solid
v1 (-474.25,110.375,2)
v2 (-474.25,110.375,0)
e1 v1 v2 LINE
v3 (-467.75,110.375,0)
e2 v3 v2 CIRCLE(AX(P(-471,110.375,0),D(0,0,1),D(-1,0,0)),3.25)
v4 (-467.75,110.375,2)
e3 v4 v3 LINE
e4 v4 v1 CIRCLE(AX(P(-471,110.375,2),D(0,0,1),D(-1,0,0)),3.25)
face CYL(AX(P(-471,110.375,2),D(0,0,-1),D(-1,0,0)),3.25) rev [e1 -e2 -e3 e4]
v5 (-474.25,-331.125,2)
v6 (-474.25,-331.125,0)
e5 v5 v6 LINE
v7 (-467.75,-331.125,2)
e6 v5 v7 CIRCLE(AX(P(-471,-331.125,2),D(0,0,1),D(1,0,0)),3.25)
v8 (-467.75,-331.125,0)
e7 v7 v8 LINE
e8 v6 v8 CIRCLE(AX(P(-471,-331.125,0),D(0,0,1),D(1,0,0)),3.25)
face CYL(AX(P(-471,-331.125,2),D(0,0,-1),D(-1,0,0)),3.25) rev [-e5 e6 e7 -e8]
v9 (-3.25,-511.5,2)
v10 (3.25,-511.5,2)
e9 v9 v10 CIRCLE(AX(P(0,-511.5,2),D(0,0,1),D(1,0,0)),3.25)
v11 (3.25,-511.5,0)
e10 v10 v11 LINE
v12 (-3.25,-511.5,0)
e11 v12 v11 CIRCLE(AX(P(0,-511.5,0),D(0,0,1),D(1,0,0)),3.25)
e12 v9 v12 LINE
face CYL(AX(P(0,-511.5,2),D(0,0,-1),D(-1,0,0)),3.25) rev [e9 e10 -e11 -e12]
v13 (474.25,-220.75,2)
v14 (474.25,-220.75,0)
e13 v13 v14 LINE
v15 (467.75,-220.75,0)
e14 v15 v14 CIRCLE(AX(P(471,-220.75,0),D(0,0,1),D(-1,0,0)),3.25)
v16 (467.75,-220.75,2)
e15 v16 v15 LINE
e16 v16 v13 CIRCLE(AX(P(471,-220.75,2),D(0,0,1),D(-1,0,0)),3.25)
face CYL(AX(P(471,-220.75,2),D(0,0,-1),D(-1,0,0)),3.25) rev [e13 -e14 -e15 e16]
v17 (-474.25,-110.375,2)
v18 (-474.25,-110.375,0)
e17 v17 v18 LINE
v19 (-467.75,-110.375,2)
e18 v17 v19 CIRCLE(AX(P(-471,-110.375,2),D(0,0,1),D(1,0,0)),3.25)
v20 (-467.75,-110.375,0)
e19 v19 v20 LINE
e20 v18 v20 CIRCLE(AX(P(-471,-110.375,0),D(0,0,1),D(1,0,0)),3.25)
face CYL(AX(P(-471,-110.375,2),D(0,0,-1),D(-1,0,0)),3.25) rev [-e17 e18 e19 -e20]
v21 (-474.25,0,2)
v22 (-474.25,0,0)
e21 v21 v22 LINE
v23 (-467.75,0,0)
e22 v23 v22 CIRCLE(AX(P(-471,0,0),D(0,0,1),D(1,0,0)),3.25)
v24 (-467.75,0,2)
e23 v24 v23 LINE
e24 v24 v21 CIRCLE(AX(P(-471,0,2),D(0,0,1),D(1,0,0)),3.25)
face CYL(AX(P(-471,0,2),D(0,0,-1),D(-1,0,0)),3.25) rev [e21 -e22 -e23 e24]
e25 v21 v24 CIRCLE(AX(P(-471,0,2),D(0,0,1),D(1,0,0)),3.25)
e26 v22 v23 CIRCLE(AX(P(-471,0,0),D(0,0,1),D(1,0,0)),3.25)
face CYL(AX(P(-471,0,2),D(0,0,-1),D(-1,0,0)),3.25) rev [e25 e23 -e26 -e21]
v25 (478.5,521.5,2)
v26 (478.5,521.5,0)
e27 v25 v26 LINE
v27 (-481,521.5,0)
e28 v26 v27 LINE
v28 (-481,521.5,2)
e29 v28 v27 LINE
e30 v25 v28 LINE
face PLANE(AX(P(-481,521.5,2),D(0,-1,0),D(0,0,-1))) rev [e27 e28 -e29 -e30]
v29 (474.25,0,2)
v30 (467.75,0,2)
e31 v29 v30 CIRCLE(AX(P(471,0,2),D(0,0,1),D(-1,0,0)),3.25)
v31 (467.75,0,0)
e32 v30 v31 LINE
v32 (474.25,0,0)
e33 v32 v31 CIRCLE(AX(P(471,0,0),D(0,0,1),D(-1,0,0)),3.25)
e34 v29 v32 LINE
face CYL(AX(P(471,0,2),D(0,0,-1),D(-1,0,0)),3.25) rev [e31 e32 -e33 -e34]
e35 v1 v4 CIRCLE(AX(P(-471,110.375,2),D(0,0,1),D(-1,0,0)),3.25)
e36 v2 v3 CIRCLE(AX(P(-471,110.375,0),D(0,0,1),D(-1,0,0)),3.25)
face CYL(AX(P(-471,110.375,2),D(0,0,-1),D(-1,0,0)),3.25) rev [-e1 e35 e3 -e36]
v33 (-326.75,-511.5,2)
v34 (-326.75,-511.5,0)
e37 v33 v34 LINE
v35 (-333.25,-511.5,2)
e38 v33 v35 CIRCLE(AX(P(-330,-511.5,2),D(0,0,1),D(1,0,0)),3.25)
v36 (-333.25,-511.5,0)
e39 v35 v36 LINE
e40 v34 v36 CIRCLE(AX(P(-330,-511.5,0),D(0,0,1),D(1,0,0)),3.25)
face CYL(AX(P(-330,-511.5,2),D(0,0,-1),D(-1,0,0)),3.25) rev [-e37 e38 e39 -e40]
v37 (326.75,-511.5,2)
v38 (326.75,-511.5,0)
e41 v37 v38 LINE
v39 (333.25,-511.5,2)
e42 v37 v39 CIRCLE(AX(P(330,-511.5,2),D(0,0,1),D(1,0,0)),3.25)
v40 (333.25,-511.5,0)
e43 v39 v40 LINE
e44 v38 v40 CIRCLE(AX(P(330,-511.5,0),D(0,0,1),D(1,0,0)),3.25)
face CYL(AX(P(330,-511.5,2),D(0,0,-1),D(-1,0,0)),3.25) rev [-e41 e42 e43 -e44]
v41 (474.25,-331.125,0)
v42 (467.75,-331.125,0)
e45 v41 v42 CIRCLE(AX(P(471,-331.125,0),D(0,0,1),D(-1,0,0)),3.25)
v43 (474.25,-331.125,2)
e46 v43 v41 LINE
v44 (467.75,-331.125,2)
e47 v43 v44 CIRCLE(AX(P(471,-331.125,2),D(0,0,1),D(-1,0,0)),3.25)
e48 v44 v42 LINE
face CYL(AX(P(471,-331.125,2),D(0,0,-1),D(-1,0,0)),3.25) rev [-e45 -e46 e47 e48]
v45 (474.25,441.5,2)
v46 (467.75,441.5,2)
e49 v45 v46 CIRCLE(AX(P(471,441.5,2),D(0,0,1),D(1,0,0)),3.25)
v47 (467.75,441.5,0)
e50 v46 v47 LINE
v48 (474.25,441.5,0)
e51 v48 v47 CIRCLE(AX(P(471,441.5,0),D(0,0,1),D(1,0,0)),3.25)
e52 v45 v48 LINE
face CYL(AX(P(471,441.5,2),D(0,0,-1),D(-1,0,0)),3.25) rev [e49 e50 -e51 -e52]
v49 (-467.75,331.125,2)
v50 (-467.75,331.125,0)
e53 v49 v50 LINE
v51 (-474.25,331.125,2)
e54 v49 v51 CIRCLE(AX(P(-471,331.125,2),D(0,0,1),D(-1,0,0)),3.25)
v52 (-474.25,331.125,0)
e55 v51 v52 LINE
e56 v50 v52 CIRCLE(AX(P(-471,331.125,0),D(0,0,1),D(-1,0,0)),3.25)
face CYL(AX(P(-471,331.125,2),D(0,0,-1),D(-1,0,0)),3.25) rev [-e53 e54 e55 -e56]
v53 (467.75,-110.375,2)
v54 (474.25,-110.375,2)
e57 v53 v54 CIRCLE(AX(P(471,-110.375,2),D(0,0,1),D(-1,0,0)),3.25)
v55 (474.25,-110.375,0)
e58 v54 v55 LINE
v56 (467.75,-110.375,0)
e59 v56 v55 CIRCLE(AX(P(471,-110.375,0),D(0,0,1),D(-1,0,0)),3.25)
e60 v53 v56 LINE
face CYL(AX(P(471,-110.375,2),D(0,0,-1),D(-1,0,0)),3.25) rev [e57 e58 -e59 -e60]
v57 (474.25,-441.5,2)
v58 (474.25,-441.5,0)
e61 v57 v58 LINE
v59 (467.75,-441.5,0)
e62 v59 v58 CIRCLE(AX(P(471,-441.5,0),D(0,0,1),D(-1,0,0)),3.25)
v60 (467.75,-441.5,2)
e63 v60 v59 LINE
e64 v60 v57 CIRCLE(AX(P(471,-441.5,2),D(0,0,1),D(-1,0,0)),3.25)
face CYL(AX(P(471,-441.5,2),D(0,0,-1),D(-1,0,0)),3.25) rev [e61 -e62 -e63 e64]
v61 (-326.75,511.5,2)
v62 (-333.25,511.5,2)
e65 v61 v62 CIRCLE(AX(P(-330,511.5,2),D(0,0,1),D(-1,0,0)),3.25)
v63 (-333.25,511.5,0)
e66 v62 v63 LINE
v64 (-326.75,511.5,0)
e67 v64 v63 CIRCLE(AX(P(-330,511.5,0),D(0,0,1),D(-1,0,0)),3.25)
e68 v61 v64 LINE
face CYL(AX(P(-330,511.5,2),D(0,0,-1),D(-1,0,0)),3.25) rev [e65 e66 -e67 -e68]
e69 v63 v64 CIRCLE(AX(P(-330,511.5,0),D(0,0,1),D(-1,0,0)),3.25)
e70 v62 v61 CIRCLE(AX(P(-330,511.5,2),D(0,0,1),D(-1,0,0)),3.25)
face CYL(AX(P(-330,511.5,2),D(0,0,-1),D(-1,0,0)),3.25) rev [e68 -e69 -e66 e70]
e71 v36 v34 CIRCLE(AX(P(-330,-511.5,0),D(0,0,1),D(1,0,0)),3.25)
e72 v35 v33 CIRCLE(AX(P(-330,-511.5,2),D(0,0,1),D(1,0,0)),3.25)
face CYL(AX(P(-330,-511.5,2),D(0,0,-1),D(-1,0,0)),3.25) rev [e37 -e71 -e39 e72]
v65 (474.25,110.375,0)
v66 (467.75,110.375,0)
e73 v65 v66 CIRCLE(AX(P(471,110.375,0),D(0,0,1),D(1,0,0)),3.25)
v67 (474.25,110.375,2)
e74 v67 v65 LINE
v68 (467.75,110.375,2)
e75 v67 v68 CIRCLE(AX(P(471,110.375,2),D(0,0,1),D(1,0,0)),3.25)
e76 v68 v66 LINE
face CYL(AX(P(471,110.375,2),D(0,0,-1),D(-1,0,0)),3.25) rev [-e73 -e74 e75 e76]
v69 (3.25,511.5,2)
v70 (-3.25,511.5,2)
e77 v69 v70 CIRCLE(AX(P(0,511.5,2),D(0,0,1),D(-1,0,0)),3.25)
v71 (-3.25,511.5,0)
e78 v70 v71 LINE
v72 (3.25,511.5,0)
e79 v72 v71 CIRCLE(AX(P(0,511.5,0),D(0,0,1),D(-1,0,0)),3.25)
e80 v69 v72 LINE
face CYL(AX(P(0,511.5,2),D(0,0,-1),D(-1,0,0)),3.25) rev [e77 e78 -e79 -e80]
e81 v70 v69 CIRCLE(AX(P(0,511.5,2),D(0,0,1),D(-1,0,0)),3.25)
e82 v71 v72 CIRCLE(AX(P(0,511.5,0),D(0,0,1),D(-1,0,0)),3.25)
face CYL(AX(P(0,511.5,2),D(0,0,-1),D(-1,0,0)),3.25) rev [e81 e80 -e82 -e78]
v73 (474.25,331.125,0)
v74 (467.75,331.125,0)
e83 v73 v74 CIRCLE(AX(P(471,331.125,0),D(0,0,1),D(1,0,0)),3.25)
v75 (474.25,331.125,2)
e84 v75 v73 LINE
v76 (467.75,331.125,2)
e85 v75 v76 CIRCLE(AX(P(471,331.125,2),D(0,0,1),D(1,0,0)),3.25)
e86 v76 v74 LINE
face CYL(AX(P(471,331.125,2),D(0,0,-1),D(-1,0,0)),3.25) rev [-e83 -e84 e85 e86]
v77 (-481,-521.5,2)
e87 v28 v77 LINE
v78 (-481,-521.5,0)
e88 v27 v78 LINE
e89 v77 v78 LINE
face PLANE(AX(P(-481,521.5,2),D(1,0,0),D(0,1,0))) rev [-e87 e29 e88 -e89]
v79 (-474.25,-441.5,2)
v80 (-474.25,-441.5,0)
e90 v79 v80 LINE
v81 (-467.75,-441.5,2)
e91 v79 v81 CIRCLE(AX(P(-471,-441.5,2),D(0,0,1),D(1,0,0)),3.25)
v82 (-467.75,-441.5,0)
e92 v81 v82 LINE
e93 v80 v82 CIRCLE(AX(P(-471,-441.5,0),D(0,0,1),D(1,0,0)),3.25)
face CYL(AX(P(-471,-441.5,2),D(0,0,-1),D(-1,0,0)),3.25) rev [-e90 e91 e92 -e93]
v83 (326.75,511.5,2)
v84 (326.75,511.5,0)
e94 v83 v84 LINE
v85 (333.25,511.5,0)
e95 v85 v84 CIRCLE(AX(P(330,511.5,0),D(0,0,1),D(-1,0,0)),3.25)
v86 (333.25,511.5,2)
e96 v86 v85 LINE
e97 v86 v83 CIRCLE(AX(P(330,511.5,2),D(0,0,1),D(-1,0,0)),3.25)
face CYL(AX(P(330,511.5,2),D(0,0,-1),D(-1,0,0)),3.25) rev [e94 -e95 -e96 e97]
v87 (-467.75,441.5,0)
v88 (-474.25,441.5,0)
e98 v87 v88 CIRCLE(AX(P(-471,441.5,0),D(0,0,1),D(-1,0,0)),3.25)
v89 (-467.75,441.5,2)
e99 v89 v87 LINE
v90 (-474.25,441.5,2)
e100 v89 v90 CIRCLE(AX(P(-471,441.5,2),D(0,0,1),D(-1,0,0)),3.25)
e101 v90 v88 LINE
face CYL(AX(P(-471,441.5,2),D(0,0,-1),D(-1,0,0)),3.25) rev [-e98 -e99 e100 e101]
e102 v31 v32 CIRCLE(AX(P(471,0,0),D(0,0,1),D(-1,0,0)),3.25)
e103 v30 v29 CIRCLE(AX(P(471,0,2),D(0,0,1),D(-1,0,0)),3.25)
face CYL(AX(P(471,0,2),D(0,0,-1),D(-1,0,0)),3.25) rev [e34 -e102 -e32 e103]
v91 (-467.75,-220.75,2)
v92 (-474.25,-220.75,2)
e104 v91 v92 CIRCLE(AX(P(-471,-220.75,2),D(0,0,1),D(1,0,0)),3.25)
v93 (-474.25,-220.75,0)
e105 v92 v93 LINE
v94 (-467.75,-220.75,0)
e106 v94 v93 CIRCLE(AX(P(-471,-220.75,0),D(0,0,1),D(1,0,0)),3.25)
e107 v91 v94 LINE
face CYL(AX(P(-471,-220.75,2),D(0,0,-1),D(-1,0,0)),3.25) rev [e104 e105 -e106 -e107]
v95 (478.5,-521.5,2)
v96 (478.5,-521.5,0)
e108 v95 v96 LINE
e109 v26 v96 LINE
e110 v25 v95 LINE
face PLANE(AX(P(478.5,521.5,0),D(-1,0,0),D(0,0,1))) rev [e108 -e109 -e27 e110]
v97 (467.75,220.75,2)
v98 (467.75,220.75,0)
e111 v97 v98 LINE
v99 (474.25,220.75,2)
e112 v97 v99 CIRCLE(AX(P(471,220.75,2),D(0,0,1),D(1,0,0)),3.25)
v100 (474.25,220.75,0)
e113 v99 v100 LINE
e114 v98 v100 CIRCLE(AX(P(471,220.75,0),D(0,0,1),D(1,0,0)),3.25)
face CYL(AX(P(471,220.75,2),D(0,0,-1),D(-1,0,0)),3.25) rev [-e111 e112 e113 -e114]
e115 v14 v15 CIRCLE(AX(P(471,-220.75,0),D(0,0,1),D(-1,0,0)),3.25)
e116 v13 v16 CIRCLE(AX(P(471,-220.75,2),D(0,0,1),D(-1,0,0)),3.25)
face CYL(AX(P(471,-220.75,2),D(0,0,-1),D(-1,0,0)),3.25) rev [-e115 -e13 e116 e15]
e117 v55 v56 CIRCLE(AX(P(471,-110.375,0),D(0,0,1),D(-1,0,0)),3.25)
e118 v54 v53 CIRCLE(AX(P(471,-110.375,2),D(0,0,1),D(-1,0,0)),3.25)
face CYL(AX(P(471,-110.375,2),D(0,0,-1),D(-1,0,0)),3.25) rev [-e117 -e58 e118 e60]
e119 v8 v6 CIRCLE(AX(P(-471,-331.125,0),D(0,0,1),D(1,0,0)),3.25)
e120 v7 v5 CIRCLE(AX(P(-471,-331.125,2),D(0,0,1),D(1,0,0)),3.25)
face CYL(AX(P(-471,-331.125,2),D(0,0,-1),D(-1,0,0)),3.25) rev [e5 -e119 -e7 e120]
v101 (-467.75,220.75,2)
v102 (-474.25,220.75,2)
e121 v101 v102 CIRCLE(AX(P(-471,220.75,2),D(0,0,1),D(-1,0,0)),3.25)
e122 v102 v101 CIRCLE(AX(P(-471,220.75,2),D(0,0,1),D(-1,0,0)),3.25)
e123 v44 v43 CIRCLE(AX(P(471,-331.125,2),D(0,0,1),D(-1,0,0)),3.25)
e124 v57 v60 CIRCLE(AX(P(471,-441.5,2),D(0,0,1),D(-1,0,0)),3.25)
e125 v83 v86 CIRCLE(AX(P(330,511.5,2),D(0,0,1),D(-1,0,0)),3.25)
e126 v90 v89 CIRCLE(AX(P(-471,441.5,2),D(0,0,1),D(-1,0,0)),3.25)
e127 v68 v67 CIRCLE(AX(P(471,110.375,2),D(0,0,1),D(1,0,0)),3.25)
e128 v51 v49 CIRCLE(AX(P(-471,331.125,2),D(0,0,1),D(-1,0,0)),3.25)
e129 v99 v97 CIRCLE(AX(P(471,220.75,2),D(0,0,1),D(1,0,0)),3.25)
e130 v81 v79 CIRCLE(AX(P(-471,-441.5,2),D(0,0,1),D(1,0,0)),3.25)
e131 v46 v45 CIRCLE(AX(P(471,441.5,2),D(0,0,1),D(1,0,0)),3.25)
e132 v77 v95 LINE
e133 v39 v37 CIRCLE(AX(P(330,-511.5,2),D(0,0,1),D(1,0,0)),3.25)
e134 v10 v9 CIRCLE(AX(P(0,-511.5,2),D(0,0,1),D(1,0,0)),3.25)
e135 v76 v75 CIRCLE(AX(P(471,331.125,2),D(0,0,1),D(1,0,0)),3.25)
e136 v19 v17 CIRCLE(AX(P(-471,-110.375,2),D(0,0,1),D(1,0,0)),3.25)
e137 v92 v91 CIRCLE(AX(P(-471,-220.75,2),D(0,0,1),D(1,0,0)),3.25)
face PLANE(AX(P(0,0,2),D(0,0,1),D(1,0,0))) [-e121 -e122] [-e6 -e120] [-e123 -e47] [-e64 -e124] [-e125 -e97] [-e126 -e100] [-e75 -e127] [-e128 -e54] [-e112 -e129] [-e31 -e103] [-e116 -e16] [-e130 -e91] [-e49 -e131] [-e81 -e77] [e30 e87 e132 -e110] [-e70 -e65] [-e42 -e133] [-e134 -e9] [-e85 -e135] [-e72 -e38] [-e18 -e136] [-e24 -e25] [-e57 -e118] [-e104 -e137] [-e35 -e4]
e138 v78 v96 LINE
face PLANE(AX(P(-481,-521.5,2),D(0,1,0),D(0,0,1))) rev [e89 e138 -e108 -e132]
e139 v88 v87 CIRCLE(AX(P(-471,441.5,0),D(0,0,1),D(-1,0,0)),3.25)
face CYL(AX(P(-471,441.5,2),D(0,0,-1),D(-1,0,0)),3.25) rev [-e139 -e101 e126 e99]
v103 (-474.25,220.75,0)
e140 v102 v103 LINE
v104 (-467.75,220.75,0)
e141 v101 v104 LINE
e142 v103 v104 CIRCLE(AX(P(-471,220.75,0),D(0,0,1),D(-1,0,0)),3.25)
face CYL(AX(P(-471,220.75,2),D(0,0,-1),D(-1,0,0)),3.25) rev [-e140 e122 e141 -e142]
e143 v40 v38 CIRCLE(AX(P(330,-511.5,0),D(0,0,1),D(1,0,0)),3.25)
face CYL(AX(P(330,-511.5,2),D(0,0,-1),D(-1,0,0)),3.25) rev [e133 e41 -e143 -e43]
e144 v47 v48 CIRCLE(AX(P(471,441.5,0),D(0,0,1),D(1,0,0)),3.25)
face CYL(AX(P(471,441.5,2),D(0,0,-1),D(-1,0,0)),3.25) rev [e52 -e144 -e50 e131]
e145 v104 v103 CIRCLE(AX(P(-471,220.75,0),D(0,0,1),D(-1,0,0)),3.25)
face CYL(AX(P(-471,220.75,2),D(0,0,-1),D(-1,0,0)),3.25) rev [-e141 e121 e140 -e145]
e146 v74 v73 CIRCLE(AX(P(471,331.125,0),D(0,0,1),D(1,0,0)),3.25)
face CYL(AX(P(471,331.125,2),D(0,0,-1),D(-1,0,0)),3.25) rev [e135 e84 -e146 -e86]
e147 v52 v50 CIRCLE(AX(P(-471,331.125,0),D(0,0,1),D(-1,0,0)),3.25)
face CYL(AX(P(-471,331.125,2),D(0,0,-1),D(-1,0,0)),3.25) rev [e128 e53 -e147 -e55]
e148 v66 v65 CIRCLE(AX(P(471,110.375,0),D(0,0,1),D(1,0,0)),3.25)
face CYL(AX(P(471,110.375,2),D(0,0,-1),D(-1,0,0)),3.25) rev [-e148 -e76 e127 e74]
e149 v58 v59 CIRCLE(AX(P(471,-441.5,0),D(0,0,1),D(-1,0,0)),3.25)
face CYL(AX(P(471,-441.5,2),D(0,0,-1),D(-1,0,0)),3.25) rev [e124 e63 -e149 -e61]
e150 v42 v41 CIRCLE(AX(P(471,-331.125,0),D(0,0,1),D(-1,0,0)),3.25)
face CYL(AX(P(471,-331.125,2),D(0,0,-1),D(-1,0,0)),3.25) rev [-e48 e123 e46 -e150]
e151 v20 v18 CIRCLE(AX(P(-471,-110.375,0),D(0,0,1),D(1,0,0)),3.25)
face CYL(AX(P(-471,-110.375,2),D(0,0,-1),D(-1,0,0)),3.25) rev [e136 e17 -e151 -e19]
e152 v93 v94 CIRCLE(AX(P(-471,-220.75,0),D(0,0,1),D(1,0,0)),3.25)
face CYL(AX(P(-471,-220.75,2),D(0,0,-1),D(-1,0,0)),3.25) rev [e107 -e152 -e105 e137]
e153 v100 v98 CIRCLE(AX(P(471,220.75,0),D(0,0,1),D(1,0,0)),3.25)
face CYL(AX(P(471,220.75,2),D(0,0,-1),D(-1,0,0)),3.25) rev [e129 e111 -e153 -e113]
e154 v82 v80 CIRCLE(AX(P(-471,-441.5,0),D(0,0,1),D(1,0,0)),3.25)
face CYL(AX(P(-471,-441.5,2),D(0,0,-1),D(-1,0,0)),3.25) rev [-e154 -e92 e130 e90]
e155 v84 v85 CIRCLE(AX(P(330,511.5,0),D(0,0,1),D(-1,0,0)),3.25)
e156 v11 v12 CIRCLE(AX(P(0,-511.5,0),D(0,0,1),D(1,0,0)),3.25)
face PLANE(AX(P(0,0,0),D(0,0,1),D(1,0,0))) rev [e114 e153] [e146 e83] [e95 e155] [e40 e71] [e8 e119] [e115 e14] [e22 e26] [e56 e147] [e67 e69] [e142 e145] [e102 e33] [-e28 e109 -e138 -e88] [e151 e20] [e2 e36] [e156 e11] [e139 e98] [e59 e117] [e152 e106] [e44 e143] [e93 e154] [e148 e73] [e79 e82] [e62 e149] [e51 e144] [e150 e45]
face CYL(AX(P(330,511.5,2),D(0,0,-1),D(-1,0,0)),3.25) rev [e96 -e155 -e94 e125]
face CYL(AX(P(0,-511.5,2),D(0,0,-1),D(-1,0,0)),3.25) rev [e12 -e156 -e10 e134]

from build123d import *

# Parameters (mm, degrees)
SKETCH_1_W          = 962
SKETCH_1_H          = 1043
SKETCH_1_R          = 3.25
EXTRUDE_1_DEPTH     = 2
SKETCH_2_W          = 2.5
SKETCH_2_H          = 2
CUT_EXTRUDE_1_DEPTH = 1149.570415778


with BuildPart() as part:
    # 草图1 → 凸台-拉伸1 (new body)
    with BuildSketch(Plane.XY):
        Rectangle(SKETCH_1_W, SKETCH_1_H)
        with Locations((-471, 0)):
            Circle(SKETCH_1_R, mode=Mode.SUBTRACT)
        with Locations((-471, -110.375)):
            Circle(SKETCH_1_R, mode=Mode.SUBTRACT)
        with Locations((-471, -220.75)):
            Circle(SKETCH_1_R, mode=Mode.SUBTRACT)
        with Locations((-471, -331.125)):
            Circle(SKETCH_1_R, mode=Mode.SUBTRACT)
        with Locations((-471, -441.5)):
            Circle(SKETCH_1_R, mode=Mode.SUBTRACT)
        with Locations((0, -511.5)):
            Circle(SKETCH_1_R, mode=Mode.SUBTRACT)
        with Locations(Location((0, 511.5, 0), (0, 0, 180))):
            Circle(SKETCH_1_R, mode=Mode.SUBTRACT)
        with Locations(Location((-471, 441.5, 0), (0, 0, 180))):
            Circle(SKETCH_1_R, mode=Mode.SUBTRACT)
        with Locations(Location((-471, 331.125, 0), (0, 0, 180))):
            Circle(SKETCH_1_R, mode=Mode.SUBTRACT)
        with Locations(Location((-471, 220.75, 0), (0, 0, 180))):
            Circle(SKETCH_1_R, mode=Mode.SUBTRACT)
        with Locations(Location((-471, 110.375, 0), (0, 0, 180))):
            Circle(SKETCH_1_R, mode=Mode.SUBTRACT)
        with Locations((471, 110.375)):
            Circle(SKETCH_1_R, mode=Mode.SUBTRACT)
        with Locations((471, 220.75)):
            Circle(SKETCH_1_R, mode=Mode.SUBTRACT)
        with Locations((471, 331.125)):
            Circle(SKETCH_1_R, mode=Mode.SUBTRACT)
        with Locations((471, 441.5)):
            Circle(SKETCH_1_R, mode=Mode.SUBTRACT)
        with Locations(Location((471, -441.5, 0), (0, 0, 180))):
            Circle(SKETCH_1_R, mode=Mode.SUBTRACT)
        with Locations(Location((471, -331.125, 0), (0, 0, 180))):
            Circle(SKETCH_1_R, mode=Mode.SUBTRACT)
        with Locations(Location((471, -220.75, 0), (0, 0, 180))):
            Circle(SKETCH_1_R, mode=Mode.SUBTRACT)
        with Locations(Location((471, -110.375, 0), (0, 0, 180))):
            Circle(SKETCH_1_R, mode=Mode.SUBTRACT)
        with Locations(Location((471, 0, 0), (0, 0, 180))):
            Circle(SKETCH_1_R, mode=Mode.SUBTRACT)
        with Locations((330, -511.5)):
            Circle(SKETCH_1_R, mode=Mode.SUBTRACT)
        with Locations((-330, -511.5)):
            Circle(SKETCH_1_R, mode=Mode.SUBTRACT)
        with Locations(Location((-330, 511.5, 0), (0, 0, 180))):
            Circle(SKETCH_1_R, mode=Mode.SUBTRACT)
        with Locations(Location((330, 511.5, 0), (0, 0, 180))):
            Circle(SKETCH_1_R, mode=Mode.SUBTRACT)
    extrude(amount=EXTRUDE_1_DEPTH)

    # 草图2 → 切除-拉伸1 (cut, through all)
    with BuildSketch(Plane.XZ.offset(521.5)):
        with Locations((479.75, 1)):
            Rectangle(SKETCH_2_W, SKETCH_2_H)
    extrude(amount=-CUT_EXTRUDE_1_DEPTH, mode=Mode.SUBTRACT)


solid = part.part
